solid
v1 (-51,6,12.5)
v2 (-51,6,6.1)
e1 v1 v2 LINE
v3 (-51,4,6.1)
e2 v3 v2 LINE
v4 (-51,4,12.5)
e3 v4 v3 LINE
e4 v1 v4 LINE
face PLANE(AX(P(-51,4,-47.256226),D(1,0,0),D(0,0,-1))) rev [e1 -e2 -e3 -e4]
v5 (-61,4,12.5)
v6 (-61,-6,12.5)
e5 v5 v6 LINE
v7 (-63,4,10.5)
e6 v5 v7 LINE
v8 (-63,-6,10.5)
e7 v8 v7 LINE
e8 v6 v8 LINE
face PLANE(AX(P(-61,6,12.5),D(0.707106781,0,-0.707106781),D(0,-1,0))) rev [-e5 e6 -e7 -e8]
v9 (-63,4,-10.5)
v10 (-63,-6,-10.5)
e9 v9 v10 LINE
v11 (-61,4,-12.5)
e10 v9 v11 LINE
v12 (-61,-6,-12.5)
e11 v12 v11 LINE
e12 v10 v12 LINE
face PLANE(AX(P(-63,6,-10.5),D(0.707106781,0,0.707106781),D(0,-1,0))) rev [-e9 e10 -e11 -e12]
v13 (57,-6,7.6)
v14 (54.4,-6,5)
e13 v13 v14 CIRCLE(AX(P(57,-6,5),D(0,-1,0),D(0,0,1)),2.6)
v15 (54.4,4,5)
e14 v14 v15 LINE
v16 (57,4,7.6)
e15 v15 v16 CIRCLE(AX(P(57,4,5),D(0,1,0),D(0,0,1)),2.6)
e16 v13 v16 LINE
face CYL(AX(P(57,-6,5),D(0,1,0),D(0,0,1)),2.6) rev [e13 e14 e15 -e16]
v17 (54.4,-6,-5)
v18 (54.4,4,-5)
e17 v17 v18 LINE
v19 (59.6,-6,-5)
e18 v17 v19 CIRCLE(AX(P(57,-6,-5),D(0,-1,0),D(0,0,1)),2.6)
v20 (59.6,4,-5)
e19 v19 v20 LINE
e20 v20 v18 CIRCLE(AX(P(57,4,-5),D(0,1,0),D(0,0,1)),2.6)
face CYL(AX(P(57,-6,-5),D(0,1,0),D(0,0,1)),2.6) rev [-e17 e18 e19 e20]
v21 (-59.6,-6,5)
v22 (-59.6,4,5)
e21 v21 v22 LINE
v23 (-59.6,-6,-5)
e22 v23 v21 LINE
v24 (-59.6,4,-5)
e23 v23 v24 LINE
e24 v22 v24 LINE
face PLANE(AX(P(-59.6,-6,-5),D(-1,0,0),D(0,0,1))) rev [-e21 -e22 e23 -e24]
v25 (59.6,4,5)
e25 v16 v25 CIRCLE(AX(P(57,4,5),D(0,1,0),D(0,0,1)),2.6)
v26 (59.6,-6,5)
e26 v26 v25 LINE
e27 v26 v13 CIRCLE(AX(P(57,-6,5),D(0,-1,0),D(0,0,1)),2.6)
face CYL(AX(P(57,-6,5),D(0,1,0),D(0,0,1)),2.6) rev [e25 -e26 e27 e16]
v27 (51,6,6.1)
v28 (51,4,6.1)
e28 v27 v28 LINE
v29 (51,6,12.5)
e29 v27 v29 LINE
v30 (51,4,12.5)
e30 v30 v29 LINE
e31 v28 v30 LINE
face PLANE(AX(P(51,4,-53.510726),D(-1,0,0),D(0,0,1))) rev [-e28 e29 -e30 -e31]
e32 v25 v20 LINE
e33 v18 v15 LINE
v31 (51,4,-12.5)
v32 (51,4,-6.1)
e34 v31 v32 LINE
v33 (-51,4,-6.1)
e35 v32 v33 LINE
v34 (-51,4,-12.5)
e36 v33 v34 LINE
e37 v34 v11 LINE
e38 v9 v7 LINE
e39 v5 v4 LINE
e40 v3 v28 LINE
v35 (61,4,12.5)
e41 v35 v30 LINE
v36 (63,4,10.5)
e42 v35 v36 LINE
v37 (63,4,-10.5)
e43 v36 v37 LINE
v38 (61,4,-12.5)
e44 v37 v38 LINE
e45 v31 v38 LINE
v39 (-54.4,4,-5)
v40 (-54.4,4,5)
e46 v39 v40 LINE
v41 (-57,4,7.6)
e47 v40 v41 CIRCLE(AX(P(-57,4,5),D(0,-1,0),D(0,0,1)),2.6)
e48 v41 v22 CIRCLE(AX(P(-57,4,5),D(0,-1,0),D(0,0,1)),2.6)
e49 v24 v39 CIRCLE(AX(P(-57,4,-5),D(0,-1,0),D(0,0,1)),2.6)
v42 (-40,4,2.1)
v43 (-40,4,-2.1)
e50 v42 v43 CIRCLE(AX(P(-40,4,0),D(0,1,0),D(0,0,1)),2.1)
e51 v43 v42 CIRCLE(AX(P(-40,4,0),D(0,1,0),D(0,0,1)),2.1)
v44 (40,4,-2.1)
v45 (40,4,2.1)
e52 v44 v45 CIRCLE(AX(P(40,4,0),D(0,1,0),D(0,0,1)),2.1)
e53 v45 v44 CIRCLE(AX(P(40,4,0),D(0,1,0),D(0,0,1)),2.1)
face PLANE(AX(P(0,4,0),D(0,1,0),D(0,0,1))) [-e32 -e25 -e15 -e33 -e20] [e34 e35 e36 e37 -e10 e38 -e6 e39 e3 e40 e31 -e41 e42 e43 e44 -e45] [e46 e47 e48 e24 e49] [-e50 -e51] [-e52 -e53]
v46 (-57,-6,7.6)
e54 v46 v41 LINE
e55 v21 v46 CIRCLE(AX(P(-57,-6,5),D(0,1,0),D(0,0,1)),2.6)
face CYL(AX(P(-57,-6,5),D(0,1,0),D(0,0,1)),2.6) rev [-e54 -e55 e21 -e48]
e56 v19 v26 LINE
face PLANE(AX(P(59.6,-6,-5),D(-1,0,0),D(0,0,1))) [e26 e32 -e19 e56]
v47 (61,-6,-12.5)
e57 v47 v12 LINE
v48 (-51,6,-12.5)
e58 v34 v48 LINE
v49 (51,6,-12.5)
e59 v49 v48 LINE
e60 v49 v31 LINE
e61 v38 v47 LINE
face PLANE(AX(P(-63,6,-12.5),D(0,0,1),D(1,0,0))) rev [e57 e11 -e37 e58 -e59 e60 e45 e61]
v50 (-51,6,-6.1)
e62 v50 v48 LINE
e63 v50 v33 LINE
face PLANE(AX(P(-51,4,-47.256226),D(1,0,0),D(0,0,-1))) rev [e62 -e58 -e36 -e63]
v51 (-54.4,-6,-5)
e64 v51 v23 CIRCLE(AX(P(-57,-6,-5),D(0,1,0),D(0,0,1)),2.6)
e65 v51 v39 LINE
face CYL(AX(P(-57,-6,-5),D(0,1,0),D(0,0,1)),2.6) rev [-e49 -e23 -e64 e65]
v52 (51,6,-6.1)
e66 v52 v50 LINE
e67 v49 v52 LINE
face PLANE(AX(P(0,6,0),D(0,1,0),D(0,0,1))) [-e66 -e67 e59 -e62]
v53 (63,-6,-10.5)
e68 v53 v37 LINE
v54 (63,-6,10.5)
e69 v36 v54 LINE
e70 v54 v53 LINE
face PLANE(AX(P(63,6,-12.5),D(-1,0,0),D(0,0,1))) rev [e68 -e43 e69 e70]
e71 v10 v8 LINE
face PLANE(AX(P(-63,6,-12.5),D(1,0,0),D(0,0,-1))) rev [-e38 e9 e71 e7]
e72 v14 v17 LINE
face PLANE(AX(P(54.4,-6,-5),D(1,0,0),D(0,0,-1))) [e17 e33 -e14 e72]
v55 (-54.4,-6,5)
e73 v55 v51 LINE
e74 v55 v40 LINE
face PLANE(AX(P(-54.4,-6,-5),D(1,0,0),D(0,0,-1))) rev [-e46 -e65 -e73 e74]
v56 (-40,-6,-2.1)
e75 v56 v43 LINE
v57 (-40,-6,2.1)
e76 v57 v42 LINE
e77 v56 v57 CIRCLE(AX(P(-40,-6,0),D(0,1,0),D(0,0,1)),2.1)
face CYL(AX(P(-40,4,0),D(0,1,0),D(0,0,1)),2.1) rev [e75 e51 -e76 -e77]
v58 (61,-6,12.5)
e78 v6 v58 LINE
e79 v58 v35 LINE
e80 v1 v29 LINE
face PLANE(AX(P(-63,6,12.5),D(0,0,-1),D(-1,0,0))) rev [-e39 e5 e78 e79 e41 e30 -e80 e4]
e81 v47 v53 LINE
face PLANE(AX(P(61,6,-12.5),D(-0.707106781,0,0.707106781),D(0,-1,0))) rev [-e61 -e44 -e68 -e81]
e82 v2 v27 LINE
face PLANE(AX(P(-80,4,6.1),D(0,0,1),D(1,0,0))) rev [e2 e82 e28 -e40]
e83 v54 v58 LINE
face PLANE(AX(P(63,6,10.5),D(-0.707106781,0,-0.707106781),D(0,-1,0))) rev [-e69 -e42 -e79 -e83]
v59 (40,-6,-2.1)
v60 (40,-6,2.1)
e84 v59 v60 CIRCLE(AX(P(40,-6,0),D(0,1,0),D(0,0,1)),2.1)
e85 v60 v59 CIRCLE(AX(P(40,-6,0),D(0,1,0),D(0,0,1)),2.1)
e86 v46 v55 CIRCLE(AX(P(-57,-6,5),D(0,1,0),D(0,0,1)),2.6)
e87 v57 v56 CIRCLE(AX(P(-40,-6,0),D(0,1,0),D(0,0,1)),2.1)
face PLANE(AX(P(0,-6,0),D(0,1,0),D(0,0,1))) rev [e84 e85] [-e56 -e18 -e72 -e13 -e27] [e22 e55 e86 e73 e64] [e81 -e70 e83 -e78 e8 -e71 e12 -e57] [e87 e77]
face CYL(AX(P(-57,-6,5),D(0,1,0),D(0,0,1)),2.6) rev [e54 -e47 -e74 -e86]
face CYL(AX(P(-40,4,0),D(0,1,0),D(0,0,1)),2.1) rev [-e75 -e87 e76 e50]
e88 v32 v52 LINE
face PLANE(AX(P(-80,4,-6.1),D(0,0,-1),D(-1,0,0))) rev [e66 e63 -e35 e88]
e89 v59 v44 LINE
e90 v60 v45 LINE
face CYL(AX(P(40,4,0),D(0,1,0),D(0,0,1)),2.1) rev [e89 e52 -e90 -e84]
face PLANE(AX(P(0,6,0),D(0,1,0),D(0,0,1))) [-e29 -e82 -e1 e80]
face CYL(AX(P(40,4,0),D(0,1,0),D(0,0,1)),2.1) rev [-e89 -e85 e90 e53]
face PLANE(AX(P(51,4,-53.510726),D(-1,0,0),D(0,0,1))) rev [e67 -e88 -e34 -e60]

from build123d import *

# Parameters (mm, degrees)
SKETCH_1_W          = 126
SKETCH_1_H          = 25
EXTRUDE_1_DEPTH     = 6
CUT_EXTRUDE_1_DEPTH = 66.339498008
SKETCH_3_W          = 160
SKETCH_3_H          = 12.2
CUT_EXTRUDE_2_DEPTH = 2
CHAMFER_1_SIZE      = 2
HOLE_WIZARD_M5_1_D  = 4.2
SKETCH_8_W          = 42.808580858
SKETCH_8_H          = 66.158715872
SKETCH_8_W_2        = 29.187668767
SKETCH_8_H_2        = 70.606360636
CUT_EXTRUDE_5_DEPTH = 2


with BuildPart() as part:
    # 草图1 → 凸台-拉伸1 (new, symmetric)
    with BuildSketch(Plane(origin=(0, 0, 0), x_dir=(1, 0, 0), z_dir=(0, 1, 0))):
        Rectangle(SKETCH_1_W, SKETCH_1_H)
    extrude(amount=EXTRUDE_1_DEPTH, both=True)

    # 草图2 → 切除-拉伸1 (cut, through all)
    with BuildSketch(Plane(origin=(0, 6, 0), x_dir=(1, 0, 0), z_dir=(0, 1, 0))):
        with BuildLine():
            Line((-54.4, 5), (-54.4, -5))
            ThreePointArc((-54.4, -5), (-57, -7.6), (-59.6, -5))
            Line((-59.6, -5), (-59.6, 5))
            ThreePointArc((-59.6, 5), (-57, 7.6), (-54.4, 5))
        make_face()
    cut_extrude_1 = extrude(amount=-CUT_EXTRUDE_1_DEPTH, mode=Mode.SUBTRACT)

    # 镜向1: 切除-拉伸1 across plane
    add(cut_extrude_1.mirror(Plane(origin=(0, 0, 0), x_dir=(0, 0, 1), z_dir=(1, 0, 0))), mode=Mode.SUBTRACT)

    # 草图3 → 切除-拉伸2 (cut)
    with BuildSketch(Plane(origin=(0, 6, 0), x_dir=(1, 0, 0), z_dir=(0, 1, 0))):
        Rectangle(SKETCH_3_W, SKETCH_3_H)
    extrude(amount=-CUT_EXTRUDE_2_DEPTH, mode=Mode.SUBTRACT)

    # 倒角1
    chamfer_1_edges = [part.edges().sort_by_distance(p)[0] for p in [
        (63, 0, 12.5),
        (-63, 0, 12.5),
        (-63, 0, -12.5),
        (63, 0, -12.5),
    ]]
    chamfer(chamfer_1_edges, length=CHAMFER_1_SIZE)

    # M5 螺纹孔1 (through all)
    with Locations(Plane(origin=(0, 4, 0), x_dir=(1, 0, 0), z_dir=(0, 1, 0))):
        with Locations((-40, 0), (40, 0)):
            Hole(HOLE_WIZARD_M5_1_D / 2)

    # 草图8 → 切除-拉伸5 (cut)
    with BuildSketch(Plane(origin=(0, 6, 0), x_dir=(1, 0, 0), z_dir=(0, 1, 0))):
        with Locations((-72.404290429, 14.176867687)):
            Rectangle(SKETCH_8_W, SKETCH_8_H)
        with Locations((65.593834383, 18.207545755)):
            Rectangle(SKETCH_8_W_2, SKETCH_8_H_2)
    extrude(amount=-CUT_EXTRUDE_5_DEPTH, mode=Mode.SUBTRACT)


solid = part.part
